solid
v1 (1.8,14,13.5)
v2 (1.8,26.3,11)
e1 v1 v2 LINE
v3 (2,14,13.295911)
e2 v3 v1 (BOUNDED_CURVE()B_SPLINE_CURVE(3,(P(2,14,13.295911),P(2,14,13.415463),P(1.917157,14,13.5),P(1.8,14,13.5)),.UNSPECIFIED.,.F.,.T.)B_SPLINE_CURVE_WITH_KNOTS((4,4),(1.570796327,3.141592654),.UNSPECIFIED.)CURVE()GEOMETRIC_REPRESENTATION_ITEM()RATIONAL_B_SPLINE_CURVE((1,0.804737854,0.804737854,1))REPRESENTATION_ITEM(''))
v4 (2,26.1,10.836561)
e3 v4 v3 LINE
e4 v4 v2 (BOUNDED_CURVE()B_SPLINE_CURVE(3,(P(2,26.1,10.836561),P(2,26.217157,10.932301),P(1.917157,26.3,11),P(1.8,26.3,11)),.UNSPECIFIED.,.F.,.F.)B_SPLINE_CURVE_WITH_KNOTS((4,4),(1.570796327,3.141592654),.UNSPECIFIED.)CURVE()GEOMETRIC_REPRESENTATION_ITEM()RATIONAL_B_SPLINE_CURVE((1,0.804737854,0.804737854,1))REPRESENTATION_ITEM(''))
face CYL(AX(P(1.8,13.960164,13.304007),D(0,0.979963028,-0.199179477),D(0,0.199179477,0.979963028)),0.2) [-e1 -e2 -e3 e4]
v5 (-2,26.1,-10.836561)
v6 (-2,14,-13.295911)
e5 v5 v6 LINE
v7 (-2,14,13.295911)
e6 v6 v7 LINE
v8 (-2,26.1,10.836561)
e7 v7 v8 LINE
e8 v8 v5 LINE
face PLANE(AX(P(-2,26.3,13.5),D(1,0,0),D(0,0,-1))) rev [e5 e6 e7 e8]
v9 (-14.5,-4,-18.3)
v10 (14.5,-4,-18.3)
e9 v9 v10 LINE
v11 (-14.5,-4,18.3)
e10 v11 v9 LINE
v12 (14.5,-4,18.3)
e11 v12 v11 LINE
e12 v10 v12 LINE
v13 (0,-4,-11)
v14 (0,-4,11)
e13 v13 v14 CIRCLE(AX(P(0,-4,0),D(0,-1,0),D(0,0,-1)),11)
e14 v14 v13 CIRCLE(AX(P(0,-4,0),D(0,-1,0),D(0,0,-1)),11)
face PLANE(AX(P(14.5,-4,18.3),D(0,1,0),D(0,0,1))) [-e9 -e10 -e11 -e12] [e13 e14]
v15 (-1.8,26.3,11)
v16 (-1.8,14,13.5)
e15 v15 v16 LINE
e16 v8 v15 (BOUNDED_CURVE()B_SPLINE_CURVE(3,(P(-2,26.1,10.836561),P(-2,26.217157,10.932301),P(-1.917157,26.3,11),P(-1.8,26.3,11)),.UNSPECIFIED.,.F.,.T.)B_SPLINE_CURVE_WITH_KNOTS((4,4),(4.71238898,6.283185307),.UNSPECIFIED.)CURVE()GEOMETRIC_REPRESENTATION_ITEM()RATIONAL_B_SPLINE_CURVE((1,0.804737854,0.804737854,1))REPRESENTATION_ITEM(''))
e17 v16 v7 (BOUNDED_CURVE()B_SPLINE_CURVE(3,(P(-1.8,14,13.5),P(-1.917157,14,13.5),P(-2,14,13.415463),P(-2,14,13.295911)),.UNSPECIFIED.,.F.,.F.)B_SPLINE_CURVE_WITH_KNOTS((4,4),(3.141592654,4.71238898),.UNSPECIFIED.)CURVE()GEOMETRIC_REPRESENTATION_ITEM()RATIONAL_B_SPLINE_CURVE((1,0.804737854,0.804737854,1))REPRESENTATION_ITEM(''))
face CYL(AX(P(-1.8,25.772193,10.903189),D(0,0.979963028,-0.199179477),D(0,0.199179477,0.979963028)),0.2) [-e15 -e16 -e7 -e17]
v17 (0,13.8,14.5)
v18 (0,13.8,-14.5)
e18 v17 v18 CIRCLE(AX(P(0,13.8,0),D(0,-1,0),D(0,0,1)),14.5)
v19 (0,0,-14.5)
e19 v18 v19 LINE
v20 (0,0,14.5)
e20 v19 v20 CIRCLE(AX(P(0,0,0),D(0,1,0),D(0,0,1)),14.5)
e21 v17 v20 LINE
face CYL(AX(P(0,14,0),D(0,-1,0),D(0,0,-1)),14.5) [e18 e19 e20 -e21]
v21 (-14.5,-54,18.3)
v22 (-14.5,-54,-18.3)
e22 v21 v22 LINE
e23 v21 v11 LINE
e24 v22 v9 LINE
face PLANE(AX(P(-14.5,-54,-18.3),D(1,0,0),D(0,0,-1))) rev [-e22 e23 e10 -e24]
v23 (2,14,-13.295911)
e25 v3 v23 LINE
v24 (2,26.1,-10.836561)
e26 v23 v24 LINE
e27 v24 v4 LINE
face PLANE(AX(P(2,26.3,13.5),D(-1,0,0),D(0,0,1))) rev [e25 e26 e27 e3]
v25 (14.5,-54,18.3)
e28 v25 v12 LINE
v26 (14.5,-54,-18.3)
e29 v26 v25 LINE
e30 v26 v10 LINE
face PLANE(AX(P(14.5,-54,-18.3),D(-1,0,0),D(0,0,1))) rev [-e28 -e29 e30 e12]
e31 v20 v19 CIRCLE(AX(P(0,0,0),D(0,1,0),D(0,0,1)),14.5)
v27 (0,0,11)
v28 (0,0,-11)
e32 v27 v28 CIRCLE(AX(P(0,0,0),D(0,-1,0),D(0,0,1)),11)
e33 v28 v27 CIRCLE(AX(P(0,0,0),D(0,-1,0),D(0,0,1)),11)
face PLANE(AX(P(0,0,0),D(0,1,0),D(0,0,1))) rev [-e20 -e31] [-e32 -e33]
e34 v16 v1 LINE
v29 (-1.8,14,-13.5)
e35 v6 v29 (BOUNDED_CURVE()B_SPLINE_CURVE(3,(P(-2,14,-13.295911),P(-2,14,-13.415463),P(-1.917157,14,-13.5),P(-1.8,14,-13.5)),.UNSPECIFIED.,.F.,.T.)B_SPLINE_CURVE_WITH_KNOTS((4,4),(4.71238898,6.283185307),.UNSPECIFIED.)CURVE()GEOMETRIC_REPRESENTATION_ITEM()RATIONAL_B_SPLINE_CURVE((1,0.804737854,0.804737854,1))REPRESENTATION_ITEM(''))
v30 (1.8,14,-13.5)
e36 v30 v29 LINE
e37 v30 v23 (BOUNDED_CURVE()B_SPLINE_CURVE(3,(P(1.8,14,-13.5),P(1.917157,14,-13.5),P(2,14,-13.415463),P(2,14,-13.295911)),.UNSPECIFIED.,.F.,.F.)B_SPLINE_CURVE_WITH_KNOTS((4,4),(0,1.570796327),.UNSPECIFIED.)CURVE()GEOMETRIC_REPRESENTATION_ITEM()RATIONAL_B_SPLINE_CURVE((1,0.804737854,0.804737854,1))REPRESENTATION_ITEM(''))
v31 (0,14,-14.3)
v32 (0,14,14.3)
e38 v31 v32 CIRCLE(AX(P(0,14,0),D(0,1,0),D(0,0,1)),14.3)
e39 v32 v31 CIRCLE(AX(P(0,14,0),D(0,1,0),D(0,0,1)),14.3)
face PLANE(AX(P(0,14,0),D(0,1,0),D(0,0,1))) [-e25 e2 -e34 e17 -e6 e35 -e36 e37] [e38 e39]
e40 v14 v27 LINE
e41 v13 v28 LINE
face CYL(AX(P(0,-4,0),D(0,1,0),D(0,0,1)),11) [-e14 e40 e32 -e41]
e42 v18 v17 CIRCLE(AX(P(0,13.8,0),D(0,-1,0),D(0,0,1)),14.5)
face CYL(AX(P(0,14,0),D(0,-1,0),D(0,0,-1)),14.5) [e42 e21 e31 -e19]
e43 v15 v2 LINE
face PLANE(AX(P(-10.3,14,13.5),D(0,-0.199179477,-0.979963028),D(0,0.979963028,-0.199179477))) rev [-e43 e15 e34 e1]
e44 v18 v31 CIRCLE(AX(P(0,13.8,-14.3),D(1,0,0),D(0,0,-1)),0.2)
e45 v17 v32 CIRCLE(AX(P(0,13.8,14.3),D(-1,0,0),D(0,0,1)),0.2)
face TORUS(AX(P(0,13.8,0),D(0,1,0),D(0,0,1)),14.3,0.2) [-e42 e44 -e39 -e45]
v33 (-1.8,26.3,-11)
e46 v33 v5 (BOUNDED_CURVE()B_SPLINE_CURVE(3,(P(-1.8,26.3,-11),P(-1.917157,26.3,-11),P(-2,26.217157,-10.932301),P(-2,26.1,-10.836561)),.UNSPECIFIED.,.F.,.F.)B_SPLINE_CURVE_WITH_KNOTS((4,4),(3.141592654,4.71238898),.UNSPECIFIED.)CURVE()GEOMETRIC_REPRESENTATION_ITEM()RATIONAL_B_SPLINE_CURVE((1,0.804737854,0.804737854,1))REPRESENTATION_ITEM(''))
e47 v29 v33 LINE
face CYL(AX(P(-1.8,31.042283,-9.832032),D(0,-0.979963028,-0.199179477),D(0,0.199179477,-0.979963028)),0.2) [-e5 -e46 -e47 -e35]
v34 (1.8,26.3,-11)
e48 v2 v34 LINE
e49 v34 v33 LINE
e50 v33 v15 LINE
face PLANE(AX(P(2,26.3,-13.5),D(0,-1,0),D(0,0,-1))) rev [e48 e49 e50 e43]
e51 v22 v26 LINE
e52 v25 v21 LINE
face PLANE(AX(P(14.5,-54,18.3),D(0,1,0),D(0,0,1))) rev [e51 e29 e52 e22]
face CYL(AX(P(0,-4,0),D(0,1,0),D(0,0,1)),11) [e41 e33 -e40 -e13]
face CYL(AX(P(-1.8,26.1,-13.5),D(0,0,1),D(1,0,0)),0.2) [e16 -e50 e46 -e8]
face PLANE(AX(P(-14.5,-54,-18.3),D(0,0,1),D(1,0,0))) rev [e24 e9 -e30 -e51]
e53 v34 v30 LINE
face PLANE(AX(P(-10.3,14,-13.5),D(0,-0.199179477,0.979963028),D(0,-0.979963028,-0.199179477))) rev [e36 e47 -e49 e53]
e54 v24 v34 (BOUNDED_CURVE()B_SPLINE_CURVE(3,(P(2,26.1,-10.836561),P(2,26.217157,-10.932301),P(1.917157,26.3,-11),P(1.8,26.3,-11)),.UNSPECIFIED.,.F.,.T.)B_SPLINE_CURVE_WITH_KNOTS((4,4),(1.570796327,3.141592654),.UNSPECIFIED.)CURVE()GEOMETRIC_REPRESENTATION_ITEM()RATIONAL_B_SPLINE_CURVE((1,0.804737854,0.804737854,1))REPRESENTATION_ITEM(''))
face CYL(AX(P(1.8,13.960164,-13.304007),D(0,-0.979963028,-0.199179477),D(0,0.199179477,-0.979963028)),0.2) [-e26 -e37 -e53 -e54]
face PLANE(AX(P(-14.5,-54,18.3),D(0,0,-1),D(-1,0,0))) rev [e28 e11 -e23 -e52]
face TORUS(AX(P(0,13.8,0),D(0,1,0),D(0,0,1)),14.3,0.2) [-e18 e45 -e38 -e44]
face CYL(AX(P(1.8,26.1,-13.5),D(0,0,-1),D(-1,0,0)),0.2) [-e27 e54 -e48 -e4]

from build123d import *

# Parameters (mm, degrees)
SKETCH2_R           = 14.5
BOSS_EXTRUDE1_DEPTH = 14
SKETCH3_W           = 4
SKETCH3_H           = 27
BOSS_EXTRUDE2_DEPTH = 12.3
CUT_EXTRUDE1_DEPTH  = 12.3
SKETCH5_R           = 11
BOSS_EXTRUDE3_DEPTH = 4
SKETCH6_W           = 29
SKETCH6_H           = 36.6
BOSS_EXTRUDE4_DEPTH = 50
FILLET1_R           = 0.2


with BuildPart() as part:
    # Sketch2 → Boss-Extrude1 (new body)
    with BuildSketch(Plane(origin=(0, 0, 0), x_dir=(1, 0, 0), z_dir=(0, 1, 0))):
        with Locations(Location((0, 0, 0), (0, 0, 270))):
            Circle(SKETCH2_R)
    extrude(amount=BOSS_EXTRUDE1_DEPTH)

    # Sketch3 → Boss-Extrude2 (add)
    with BuildSketch(Plane(origin=(0, 14, 0), x_dir=(1, 0, 0), z_dir=(0, 1, 0))):
        Rectangle(SKETCH3_W, SKETCH3_H)
    extrude(amount=BOSS_EXTRUDE2_DEPTH)

    # Sketch4 → Cut-Extrude1 (cut)
    with BuildSketch(Plane(origin=(2, 0, 0), x_dir=(0, 0, -1), z_dir=(1, 0, 0))):
        Polygon((-13.5, 26.3), (-13.5, 14), (-11, 26.3), align=None)
        Polygon((11, 26.3), (13.5, 26.3), (13.5, 14), align=None)
    extrude(amount=-CUT_EXTRUDE1_DEPTH, mode=Mode.SUBTRACT)

    # Sketch5 → Boss-Extrude3 (add)
    with BuildSketch(Plane.XZ):
        with Locations(Location((0, 0, 0), (0, 0, 90))):
            Circle(SKETCH5_R)
    extrude(amount=BOSS_EXTRUDE3_DEPTH)

    # Sketch6 → Boss-Extrude4 (add)
    with BuildSketch(Plane.XZ.offset(4)):
        Rectangle(SKETCH6_W, SKETCH6_H)
    extrude(amount=BOSS_EXTRUDE4_DEPTH)

    # Fillet1
    fillet1_edges = [part.edges().sort_by_distance(p)[0] for p in [
        (2, 26.3, 0),
        (-2, 20.15, 12.25),
        (2, 20.15, 12.25),
        (-2, 26.3, 0),
        (-2, 20.15, -12.25),
        (2, 20.15, -12.25),
        (0, 14, -14.5),
    ]]
    fillet(fillet1_edges, radius=FILLET1_R)


solid = part.part
